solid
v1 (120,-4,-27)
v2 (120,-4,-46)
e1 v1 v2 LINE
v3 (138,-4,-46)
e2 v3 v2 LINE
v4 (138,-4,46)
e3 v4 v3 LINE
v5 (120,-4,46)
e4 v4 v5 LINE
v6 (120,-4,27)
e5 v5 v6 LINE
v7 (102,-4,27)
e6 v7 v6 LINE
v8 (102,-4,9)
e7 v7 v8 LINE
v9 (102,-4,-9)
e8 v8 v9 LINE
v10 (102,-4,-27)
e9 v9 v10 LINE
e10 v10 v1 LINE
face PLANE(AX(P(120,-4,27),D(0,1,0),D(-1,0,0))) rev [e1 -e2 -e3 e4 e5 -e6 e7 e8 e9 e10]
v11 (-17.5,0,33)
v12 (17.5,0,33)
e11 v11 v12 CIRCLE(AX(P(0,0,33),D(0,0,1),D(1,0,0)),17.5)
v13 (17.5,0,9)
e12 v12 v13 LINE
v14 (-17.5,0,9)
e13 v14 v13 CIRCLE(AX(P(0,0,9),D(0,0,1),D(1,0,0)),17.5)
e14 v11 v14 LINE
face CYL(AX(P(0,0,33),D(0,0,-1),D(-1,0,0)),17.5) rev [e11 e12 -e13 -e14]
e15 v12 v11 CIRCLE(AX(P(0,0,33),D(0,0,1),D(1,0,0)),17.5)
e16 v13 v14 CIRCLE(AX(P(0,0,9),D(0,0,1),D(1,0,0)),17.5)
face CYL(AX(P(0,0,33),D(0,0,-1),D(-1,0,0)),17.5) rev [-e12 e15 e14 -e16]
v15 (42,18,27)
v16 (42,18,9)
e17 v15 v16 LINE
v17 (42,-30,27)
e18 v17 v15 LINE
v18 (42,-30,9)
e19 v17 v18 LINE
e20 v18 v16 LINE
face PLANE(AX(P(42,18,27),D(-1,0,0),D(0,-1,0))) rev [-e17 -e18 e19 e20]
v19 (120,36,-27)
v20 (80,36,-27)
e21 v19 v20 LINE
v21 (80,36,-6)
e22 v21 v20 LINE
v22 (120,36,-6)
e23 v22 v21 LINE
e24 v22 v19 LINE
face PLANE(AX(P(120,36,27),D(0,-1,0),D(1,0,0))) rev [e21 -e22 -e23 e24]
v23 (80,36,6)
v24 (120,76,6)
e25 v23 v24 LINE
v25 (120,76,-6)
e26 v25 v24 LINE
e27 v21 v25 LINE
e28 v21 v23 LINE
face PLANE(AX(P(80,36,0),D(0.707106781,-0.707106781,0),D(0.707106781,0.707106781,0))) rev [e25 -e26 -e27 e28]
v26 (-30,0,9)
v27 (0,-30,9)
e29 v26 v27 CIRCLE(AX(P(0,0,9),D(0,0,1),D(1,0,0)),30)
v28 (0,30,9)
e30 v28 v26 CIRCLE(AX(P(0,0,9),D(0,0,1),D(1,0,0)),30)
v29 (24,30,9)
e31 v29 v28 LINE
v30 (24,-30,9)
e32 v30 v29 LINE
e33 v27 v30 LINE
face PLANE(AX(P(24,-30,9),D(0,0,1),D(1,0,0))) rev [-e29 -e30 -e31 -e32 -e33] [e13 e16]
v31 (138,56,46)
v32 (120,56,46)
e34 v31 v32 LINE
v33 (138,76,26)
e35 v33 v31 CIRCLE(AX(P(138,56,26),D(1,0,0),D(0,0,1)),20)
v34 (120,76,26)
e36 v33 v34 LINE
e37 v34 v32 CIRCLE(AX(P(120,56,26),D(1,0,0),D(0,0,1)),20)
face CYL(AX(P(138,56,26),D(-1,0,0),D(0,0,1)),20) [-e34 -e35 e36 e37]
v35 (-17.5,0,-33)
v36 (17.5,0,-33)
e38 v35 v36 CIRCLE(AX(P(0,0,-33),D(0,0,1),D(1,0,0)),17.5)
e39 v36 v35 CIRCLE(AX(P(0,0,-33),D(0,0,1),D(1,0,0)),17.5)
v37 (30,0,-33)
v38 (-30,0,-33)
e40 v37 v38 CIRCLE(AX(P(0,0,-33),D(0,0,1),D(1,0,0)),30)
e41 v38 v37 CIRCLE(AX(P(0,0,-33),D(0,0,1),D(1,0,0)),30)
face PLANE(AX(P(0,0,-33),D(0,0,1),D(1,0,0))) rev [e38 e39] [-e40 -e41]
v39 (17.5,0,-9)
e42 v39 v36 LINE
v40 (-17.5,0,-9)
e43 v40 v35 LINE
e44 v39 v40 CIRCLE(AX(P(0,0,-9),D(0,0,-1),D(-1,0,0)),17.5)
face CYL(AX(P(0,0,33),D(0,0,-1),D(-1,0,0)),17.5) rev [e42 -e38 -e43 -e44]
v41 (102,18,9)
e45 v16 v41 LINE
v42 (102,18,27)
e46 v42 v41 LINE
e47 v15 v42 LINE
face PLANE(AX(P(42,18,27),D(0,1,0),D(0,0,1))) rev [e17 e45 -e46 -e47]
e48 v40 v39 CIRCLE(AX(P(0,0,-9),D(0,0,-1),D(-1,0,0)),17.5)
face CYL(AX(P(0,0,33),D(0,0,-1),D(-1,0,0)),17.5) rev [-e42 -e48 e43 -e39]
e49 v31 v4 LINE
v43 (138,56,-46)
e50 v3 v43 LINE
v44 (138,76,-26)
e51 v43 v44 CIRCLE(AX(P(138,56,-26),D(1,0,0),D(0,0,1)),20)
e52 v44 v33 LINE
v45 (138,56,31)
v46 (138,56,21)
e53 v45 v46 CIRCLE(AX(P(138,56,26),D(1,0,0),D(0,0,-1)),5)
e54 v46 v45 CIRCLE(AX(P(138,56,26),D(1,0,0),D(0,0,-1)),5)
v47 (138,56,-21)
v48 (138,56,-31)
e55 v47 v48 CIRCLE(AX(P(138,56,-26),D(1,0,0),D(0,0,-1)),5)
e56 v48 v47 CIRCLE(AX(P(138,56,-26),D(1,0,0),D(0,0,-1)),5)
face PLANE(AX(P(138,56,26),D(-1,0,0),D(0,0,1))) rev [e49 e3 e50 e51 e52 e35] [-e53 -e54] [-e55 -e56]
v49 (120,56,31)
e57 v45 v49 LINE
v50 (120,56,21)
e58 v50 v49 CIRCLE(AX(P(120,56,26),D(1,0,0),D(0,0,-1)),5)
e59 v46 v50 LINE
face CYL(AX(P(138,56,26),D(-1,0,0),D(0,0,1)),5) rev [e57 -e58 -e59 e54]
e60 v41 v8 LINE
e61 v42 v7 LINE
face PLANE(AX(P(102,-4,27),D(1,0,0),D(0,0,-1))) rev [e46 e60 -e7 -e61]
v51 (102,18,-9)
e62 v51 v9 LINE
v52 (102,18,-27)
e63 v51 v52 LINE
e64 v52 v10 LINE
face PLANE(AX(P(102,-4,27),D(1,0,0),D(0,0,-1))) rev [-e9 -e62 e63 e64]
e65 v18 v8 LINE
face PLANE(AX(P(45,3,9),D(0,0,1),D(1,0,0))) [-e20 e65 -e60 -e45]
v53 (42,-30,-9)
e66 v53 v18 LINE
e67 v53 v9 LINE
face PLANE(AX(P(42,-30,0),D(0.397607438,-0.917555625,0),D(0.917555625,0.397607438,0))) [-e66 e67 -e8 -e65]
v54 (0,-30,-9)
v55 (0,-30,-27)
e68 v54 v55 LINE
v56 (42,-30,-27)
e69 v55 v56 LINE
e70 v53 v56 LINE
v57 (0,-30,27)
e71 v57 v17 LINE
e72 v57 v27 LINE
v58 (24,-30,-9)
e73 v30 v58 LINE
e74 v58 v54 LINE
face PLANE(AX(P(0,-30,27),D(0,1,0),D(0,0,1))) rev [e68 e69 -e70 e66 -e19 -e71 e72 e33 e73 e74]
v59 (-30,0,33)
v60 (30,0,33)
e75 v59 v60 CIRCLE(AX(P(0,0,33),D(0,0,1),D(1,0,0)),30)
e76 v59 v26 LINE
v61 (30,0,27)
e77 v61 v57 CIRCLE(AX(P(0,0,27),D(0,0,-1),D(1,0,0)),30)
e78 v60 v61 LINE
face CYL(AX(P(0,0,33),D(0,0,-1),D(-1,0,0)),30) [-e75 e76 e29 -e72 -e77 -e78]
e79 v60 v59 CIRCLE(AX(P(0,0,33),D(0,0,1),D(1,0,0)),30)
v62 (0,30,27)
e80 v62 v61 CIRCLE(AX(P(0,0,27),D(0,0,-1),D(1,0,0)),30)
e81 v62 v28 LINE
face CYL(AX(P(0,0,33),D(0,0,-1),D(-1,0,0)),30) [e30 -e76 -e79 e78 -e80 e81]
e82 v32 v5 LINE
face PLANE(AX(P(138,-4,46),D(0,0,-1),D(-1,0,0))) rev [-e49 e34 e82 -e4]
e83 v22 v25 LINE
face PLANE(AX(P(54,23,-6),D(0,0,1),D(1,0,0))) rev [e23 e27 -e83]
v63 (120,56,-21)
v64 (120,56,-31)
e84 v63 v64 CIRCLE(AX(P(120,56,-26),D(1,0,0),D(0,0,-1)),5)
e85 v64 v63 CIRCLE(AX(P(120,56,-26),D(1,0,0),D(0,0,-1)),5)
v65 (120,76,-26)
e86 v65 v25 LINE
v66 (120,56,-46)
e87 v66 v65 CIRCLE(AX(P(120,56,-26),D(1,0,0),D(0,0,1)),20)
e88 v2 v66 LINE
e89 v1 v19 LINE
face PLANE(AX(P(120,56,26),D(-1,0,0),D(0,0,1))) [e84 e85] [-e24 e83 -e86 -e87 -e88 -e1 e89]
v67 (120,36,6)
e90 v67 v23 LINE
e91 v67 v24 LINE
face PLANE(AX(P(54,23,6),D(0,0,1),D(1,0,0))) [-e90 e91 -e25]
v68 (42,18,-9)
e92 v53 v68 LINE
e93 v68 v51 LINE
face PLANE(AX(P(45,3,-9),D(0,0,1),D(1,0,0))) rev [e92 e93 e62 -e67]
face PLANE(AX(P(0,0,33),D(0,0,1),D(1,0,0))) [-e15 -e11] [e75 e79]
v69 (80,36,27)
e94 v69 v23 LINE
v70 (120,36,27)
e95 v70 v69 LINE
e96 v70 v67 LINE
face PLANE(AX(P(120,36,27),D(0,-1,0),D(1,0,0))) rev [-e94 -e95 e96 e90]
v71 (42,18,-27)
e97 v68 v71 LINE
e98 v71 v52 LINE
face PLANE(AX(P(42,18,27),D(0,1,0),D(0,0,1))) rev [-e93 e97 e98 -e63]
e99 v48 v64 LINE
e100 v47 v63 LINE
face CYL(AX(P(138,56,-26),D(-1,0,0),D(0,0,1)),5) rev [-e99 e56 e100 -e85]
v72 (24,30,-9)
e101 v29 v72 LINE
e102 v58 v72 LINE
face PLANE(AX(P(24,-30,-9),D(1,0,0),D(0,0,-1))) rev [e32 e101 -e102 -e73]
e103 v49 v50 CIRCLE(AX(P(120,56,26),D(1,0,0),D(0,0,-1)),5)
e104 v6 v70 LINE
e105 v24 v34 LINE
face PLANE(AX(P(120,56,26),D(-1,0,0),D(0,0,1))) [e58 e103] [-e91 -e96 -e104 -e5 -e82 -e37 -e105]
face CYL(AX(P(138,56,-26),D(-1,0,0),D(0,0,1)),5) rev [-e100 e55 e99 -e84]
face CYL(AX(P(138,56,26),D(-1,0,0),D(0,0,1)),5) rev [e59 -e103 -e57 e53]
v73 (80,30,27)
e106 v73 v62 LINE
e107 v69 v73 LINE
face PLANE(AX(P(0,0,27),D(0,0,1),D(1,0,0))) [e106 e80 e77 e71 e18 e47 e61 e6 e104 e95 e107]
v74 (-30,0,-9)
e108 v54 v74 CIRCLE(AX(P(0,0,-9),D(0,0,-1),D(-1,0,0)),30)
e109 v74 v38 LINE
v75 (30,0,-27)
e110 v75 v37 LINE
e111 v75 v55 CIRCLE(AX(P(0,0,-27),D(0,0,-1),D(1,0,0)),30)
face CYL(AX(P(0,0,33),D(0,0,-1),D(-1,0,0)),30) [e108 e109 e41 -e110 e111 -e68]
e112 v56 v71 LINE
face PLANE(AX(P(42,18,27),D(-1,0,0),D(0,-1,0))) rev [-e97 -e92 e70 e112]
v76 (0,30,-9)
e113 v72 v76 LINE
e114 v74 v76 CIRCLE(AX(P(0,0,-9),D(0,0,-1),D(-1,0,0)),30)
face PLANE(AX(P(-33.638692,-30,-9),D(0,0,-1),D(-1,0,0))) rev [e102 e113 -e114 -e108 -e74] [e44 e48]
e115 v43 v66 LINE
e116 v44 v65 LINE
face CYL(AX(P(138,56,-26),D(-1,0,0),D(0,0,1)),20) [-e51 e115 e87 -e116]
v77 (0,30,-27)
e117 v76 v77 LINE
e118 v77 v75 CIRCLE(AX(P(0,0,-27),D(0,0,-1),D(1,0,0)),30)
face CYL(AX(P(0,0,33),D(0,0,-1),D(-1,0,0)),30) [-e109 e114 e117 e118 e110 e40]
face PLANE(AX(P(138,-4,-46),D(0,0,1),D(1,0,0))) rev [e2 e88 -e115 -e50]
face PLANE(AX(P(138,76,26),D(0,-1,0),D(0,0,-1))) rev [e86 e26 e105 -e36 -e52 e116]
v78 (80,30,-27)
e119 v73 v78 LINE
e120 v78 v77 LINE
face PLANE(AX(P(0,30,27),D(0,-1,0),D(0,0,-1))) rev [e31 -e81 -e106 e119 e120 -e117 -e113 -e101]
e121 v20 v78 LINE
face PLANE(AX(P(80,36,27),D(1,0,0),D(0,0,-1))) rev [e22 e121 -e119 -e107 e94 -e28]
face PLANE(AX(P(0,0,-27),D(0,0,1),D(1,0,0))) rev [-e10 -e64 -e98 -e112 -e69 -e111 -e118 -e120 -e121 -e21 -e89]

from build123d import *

# Parameters (mm, degrees)
HUB_PROFILE_R                = 30
HUB_PROFILE_R_2              = 17.5
BEARING_HUB_60_BORE_35_DEPTH = 33
SUPPORT_ARM_DEPTH            = 27
HUB_RIB_18_REACH             = 131.557
HUB_RIB_SKETCH_WALL_W        = 326.505005478
HUB_RIB_SKETCH_WALL_H        = 18
MOUNTING_PLATE_PROFILE_R     = 5
MOUNTING_PLATE_DEPTH         = 18
PLATE_RIB_12_REACH           = 166.122
PLATE_RIB_SKETCH_WALL_W      = 386.812354318
PLATE_RIB_SKETCH_WALL_H      = 12
FORK_SLOT_PROFILE_W          = 57.638691925
FORK_SLOT_PROFILE_H          = 18
FORK_SLOT_24X18_DEPTH        = 158.353106102


with BuildPart() as part:
    # Hub Profile → Bearing Hub Ø60 Bore Ø35 (new, symmetric)
    with BuildSketch(Plane.XY):
        Circle(HUB_PROFILE_R)
        Circle(HUB_PROFILE_R_2, mode=Mode.SUBTRACT)
    extrude(amount=BEARING_HUB_60_BORE_35_DEPTH, both=True)

    # Support Arm Profile → Support Arm (add, symmetric)
    with BuildSketch(Plane.XY):
        with BuildLine():
            Line((0, 30), (45.688517283, 30))
            Line((45.688517283, 30), (80, 30))
            Line((80, 30), (80, 36))
            Line((80, 36), (120, 36))
            Line((120, 36), (120, -4))
            Line((120, -4), (102, -4))
            Line((102, -4), (102, 18))
            Line((102, 18), (42, 18))
            Line((42, 18), (42, -30))
            Line((42, -30), (0, -30))
            ThreePointArc((0, -30), (30, 0), (0, 30))
        make_face()
    extrude(amount=SUPPORT_ARM_DEPTH, both=True)

    # Hub Rib Sketch wall → Hub Rib 18 (add, up to next)
    with BuildSketch(Plane(origin=(72, -17, 0), x_dir=(0.91755562531, 0.397607437634, 0), z_dir=(-0.397607437634, 0.91755562531, 0)), mode=Mode.PRIVATE) as hub_rib_18_sk1:
        Rectangle(HUB_RIB_SKETCH_WALL_W, HUB_RIB_SKETCH_WALL_H)
    hub_rib_18_tool1 = extrude(hub_rib_18_sk1.sketch, amount=HUB_RIB_18_REACH, mode=Mode.PRIVATE) - part.part
    add(hub_rib_18_tool1.solids().sort_by_distance((72, -17, 0))[0])

    # Mounting Plate Profile → Mounting Plate (add)
    with BuildSketch(Plane(origin=(120, 0, 0), x_dir=(0, 0, -1), z_dir=(1, 0, 0))):
        with BuildLine():
            Line((-46, -4), (46, -4))
            Line((46, -4), (46, 56))
            ThreePointArc((46, 56), (40.142135624, 70.142135624), (26, 76))
            Line((26, 76), (-26, 76))
            ThreePointArc((-26, 76), (-40.142135624, 70.142135624), (-46, 56))
            Line((-46, 56), (-46, -4))
        make_face()
        with Locations((-26, 56)):
            Circle(MOUNTING_PLATE_PROFILE_R, mode=Mode.SUBTRACT)
        with Locations((26, 56)):
            Circle(MOUNTING_PLATE_PROFILE_R, mode=Mode.SUBTRACT)
    extrude(amount=MOUNTING_PLATE_DEPTH)

    # Plate Rib Sketch wall → Plate Rib 12 (add, up to next)
    with BuildSketch(Plane(origin=(100, 56, 0), x_dir=(0.707106781187, 0.707106781187, 0), z_dir=(-0.707106781187, 0.707106781187, 0)), mode=Mode.PRIVATE) as plate_rib_12_sk1:
        Rectangle(PLATE_RIB_SKETCH_WALL_W, PLATE_RIB_SKETCH_WALL_H)
    plate_rib_12_tool1 = extrude(plate_rib_12_sk1.sketch, amount=-PLATE_RIB_12_REACH, mode=Mode.PRIVATE) - part.part
    add(plate_rib_12_tool1.solids().sort_by_distance((100, 56, 0))[0])

    # Fork Slot Profile → Fork Slot 24x18 (cut, through all)
    with BuildSketch(Plane(origin=(0, 30, 0), x_dir=(1, 0, 0), z_dir=(0, 1, 0))):
        with Locations((-4.819345963, 0)):
            Rectangle(FORK_SLOT_PROFILE_W, FORK_SLOT_PROFILE_H)
    extrude(amount=-FORK_SLOT_24X18_DEPTH, mode=Mode.SUBTRACT)


solid = part.part
